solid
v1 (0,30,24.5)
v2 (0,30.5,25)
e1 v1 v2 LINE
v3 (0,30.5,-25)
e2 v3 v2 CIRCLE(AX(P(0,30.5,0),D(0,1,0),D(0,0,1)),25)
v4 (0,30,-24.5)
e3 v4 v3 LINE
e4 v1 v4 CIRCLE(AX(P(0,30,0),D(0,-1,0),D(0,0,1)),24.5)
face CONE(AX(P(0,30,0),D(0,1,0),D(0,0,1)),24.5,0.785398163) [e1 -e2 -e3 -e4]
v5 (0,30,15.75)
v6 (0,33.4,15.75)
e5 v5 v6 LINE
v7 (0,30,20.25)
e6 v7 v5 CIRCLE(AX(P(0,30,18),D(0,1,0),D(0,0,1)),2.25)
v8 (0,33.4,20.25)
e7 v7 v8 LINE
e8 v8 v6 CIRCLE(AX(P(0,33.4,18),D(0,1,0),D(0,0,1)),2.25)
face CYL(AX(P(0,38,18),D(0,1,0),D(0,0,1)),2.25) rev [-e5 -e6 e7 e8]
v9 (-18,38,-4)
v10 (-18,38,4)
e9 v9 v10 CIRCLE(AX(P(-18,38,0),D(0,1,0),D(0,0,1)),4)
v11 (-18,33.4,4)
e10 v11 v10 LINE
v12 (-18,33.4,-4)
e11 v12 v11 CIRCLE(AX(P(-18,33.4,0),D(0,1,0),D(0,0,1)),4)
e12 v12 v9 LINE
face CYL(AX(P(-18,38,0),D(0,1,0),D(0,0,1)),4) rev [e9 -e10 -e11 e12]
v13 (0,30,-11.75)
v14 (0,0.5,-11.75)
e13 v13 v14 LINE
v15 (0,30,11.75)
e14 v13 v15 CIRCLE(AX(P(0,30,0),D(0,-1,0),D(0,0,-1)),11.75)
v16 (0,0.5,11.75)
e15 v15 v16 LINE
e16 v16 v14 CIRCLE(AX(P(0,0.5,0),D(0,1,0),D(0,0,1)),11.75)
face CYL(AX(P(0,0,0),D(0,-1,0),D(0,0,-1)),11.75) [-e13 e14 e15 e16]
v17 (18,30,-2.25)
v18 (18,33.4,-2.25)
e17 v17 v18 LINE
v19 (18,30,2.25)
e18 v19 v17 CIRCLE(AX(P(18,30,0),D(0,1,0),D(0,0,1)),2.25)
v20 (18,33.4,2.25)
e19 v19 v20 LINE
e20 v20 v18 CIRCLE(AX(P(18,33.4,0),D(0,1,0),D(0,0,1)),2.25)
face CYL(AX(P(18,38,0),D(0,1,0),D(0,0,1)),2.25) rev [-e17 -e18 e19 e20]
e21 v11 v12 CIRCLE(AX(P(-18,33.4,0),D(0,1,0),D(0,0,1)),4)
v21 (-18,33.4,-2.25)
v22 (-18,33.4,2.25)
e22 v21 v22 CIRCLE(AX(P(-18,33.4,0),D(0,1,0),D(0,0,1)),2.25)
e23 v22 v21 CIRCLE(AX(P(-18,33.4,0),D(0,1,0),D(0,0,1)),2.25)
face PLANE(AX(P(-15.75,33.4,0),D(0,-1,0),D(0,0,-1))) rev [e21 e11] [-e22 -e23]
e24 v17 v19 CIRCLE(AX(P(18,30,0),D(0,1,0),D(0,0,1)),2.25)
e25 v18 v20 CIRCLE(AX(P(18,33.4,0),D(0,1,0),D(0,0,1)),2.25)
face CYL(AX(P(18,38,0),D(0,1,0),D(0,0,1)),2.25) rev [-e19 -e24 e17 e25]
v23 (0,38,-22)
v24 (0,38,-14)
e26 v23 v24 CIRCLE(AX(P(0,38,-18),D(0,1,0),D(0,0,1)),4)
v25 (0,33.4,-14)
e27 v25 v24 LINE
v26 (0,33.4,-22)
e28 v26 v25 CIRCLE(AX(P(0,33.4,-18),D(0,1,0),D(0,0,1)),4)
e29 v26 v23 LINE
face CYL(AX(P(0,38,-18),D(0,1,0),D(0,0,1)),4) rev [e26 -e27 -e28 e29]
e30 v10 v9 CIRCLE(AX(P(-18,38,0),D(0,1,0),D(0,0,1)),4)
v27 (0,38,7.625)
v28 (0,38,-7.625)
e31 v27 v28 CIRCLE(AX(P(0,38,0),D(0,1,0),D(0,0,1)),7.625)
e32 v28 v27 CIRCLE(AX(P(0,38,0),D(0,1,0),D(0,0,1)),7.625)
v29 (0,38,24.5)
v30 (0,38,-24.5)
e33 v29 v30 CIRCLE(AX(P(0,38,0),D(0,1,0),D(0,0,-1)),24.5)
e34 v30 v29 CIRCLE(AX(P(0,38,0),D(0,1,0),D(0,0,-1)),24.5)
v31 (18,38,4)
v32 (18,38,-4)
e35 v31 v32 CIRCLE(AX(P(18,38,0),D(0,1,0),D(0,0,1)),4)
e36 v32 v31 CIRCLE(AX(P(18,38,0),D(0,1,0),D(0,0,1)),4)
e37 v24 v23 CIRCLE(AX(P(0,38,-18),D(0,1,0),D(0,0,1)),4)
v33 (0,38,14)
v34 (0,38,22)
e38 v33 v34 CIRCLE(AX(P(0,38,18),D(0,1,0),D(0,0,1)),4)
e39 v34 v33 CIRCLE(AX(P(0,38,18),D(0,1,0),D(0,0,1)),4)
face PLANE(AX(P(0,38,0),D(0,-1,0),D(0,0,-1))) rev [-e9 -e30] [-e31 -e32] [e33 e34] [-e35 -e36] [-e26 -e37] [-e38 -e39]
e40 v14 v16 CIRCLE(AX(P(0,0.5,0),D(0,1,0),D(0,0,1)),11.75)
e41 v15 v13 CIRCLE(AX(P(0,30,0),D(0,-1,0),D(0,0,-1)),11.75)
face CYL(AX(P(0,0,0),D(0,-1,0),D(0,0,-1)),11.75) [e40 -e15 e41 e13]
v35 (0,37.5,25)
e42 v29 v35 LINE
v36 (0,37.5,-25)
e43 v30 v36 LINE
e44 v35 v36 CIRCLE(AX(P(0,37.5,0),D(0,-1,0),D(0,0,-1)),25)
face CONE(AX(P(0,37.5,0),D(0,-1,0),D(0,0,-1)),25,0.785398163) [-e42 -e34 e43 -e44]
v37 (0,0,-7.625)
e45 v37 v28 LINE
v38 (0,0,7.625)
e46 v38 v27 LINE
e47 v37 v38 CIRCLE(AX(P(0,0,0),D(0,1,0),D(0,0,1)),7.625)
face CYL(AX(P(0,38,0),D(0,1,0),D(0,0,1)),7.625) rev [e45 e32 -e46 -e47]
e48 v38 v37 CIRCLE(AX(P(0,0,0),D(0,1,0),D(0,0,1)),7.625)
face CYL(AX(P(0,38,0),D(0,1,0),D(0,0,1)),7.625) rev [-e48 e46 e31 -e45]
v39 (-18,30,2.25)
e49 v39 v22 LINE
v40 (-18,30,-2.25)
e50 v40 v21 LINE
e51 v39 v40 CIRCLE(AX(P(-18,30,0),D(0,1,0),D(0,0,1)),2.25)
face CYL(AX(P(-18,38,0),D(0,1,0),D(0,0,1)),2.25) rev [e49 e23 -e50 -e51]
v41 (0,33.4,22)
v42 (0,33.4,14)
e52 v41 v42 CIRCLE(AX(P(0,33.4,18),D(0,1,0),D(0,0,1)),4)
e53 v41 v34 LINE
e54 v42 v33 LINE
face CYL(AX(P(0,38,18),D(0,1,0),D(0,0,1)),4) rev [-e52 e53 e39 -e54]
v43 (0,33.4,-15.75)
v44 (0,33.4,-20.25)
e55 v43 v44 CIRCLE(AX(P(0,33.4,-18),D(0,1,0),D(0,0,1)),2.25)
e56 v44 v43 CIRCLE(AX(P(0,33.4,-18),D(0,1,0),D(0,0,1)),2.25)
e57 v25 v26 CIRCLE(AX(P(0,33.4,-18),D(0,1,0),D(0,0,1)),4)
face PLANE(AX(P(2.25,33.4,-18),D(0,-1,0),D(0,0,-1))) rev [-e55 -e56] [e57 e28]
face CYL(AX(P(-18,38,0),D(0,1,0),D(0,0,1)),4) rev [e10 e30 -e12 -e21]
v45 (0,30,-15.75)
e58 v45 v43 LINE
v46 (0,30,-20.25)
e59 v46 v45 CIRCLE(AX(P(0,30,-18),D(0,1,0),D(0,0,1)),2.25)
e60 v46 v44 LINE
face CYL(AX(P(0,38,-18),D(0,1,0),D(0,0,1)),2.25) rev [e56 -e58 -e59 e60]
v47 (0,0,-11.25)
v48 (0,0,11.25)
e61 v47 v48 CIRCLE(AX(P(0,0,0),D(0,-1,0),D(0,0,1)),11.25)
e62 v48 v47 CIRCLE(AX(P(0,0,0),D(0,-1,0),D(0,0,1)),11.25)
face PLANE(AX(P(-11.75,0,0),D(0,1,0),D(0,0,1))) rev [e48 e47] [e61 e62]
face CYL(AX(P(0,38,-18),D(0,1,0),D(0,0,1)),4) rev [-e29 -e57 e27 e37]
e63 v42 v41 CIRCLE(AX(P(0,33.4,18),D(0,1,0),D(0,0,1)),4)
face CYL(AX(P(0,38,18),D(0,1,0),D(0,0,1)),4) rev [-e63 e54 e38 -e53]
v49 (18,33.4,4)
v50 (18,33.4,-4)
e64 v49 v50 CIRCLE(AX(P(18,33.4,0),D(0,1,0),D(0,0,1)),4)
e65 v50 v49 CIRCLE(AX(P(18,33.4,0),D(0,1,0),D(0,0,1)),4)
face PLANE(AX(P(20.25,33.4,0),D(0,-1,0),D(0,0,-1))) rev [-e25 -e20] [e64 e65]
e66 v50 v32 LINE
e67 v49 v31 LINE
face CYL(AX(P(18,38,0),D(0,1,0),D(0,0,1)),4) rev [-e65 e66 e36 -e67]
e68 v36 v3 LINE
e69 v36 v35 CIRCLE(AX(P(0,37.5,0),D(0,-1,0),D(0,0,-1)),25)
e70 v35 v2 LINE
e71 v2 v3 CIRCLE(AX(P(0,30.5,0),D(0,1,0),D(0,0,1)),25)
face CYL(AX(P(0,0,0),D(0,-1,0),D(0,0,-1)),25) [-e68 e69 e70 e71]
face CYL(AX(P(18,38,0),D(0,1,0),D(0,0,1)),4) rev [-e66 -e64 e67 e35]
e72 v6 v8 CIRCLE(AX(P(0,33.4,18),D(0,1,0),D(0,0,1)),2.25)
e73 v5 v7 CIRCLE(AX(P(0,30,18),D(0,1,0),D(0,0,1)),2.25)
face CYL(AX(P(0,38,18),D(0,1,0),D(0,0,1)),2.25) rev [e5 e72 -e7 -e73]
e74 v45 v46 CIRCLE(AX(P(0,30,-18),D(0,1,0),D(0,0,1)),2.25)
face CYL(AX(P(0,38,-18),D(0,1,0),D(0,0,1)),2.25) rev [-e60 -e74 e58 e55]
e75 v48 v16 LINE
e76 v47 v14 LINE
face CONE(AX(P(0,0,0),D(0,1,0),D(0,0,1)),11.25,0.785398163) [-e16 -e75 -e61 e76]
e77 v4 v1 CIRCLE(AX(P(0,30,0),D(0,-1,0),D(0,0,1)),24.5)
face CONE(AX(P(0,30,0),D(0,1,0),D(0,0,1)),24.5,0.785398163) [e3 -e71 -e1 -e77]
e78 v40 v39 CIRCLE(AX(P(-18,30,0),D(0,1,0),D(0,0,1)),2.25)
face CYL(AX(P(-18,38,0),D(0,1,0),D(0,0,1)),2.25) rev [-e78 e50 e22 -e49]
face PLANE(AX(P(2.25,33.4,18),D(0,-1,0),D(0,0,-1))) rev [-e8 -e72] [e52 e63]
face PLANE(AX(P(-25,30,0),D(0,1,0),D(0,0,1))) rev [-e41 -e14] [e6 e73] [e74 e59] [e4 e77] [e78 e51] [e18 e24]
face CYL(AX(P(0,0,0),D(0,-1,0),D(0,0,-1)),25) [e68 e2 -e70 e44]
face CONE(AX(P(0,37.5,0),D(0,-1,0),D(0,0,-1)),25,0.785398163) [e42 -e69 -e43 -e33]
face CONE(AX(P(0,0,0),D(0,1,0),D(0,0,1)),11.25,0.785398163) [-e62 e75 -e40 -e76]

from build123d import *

# Parameters (mm, degrees)
G3_8_TAPPED_HOLE1_D                                 = 15.25
HOLE_SIZE_PER_SOCKET_HEAD_CAP_SCREW_TYP_D           = 4.5
HOLE_SIZE_PER_SOCKET_HEAD_CAP_SCREW_TYP_CBORE_D     = 8
HOLE_SIZE_PER_SOCKET_HEAD_CAP_SCREW_TYP_CBORE_DEPTH = 4.6
CHAMFER1_SIZE                                       = 0.5


with BuildPart() as part:
    # Sketch1 → Revolve1 (revolve)
    with BuildSketch(Plane.XY, mode=Mode.PRIVATE) as revolve1_sk:
        Polygon((0, 38), (-25, 38), (-25, 30), (-11.75, 30), (-11.75, 0), (0, 0), align=None)
    revolve(revolve1_sk.sketch.rotate(Axis((0, 0, 0), (0, 1, 0)), 270), axis=Axis((0, 0, 0), (0, 1, 0)))

    # G3/8 Tapped Hole1 (through all)
    with Locations(Plane.ZX.offset(38)):
        with Locations((0, 0)):
            Hole(G3_8_TAPPED_HOLE1_D / 2)

    # Hole Size (per socket head cap screw type)1 (through all)
    with Locations(Plane(origin=(0, 38, -18), x_dir=(0, 0, 1), z_dir=(0, 1, 0))):
        with Locations((0, 0), (18, -18), (18, 18), (36, 0)):
            CounterBoreHole(HOLE_SIZE_PER_SOCKET_HEAD_CAP_SCREW_TYP_D / 2, HOLE_SIZE_PER_SOCKET_HEAD_CAP_SCREW_TYP_CBORE_D / 2, HOLE_SIZE_PER_SOCKET_HEAD_CAP_SCREW_TYP_CBORE_DEPTH)

    # Chamfer1
    chamfer1_edges = [part.edges().sort_by_distance(p)[0] for p in [
        (0, 0, 11.75),
        (0, 30, 25),
        (0, 38, 25),
    ]]
    chamfer(chamfer1_edges, length=CHAMFER1_SIZE)


solid = part.part
